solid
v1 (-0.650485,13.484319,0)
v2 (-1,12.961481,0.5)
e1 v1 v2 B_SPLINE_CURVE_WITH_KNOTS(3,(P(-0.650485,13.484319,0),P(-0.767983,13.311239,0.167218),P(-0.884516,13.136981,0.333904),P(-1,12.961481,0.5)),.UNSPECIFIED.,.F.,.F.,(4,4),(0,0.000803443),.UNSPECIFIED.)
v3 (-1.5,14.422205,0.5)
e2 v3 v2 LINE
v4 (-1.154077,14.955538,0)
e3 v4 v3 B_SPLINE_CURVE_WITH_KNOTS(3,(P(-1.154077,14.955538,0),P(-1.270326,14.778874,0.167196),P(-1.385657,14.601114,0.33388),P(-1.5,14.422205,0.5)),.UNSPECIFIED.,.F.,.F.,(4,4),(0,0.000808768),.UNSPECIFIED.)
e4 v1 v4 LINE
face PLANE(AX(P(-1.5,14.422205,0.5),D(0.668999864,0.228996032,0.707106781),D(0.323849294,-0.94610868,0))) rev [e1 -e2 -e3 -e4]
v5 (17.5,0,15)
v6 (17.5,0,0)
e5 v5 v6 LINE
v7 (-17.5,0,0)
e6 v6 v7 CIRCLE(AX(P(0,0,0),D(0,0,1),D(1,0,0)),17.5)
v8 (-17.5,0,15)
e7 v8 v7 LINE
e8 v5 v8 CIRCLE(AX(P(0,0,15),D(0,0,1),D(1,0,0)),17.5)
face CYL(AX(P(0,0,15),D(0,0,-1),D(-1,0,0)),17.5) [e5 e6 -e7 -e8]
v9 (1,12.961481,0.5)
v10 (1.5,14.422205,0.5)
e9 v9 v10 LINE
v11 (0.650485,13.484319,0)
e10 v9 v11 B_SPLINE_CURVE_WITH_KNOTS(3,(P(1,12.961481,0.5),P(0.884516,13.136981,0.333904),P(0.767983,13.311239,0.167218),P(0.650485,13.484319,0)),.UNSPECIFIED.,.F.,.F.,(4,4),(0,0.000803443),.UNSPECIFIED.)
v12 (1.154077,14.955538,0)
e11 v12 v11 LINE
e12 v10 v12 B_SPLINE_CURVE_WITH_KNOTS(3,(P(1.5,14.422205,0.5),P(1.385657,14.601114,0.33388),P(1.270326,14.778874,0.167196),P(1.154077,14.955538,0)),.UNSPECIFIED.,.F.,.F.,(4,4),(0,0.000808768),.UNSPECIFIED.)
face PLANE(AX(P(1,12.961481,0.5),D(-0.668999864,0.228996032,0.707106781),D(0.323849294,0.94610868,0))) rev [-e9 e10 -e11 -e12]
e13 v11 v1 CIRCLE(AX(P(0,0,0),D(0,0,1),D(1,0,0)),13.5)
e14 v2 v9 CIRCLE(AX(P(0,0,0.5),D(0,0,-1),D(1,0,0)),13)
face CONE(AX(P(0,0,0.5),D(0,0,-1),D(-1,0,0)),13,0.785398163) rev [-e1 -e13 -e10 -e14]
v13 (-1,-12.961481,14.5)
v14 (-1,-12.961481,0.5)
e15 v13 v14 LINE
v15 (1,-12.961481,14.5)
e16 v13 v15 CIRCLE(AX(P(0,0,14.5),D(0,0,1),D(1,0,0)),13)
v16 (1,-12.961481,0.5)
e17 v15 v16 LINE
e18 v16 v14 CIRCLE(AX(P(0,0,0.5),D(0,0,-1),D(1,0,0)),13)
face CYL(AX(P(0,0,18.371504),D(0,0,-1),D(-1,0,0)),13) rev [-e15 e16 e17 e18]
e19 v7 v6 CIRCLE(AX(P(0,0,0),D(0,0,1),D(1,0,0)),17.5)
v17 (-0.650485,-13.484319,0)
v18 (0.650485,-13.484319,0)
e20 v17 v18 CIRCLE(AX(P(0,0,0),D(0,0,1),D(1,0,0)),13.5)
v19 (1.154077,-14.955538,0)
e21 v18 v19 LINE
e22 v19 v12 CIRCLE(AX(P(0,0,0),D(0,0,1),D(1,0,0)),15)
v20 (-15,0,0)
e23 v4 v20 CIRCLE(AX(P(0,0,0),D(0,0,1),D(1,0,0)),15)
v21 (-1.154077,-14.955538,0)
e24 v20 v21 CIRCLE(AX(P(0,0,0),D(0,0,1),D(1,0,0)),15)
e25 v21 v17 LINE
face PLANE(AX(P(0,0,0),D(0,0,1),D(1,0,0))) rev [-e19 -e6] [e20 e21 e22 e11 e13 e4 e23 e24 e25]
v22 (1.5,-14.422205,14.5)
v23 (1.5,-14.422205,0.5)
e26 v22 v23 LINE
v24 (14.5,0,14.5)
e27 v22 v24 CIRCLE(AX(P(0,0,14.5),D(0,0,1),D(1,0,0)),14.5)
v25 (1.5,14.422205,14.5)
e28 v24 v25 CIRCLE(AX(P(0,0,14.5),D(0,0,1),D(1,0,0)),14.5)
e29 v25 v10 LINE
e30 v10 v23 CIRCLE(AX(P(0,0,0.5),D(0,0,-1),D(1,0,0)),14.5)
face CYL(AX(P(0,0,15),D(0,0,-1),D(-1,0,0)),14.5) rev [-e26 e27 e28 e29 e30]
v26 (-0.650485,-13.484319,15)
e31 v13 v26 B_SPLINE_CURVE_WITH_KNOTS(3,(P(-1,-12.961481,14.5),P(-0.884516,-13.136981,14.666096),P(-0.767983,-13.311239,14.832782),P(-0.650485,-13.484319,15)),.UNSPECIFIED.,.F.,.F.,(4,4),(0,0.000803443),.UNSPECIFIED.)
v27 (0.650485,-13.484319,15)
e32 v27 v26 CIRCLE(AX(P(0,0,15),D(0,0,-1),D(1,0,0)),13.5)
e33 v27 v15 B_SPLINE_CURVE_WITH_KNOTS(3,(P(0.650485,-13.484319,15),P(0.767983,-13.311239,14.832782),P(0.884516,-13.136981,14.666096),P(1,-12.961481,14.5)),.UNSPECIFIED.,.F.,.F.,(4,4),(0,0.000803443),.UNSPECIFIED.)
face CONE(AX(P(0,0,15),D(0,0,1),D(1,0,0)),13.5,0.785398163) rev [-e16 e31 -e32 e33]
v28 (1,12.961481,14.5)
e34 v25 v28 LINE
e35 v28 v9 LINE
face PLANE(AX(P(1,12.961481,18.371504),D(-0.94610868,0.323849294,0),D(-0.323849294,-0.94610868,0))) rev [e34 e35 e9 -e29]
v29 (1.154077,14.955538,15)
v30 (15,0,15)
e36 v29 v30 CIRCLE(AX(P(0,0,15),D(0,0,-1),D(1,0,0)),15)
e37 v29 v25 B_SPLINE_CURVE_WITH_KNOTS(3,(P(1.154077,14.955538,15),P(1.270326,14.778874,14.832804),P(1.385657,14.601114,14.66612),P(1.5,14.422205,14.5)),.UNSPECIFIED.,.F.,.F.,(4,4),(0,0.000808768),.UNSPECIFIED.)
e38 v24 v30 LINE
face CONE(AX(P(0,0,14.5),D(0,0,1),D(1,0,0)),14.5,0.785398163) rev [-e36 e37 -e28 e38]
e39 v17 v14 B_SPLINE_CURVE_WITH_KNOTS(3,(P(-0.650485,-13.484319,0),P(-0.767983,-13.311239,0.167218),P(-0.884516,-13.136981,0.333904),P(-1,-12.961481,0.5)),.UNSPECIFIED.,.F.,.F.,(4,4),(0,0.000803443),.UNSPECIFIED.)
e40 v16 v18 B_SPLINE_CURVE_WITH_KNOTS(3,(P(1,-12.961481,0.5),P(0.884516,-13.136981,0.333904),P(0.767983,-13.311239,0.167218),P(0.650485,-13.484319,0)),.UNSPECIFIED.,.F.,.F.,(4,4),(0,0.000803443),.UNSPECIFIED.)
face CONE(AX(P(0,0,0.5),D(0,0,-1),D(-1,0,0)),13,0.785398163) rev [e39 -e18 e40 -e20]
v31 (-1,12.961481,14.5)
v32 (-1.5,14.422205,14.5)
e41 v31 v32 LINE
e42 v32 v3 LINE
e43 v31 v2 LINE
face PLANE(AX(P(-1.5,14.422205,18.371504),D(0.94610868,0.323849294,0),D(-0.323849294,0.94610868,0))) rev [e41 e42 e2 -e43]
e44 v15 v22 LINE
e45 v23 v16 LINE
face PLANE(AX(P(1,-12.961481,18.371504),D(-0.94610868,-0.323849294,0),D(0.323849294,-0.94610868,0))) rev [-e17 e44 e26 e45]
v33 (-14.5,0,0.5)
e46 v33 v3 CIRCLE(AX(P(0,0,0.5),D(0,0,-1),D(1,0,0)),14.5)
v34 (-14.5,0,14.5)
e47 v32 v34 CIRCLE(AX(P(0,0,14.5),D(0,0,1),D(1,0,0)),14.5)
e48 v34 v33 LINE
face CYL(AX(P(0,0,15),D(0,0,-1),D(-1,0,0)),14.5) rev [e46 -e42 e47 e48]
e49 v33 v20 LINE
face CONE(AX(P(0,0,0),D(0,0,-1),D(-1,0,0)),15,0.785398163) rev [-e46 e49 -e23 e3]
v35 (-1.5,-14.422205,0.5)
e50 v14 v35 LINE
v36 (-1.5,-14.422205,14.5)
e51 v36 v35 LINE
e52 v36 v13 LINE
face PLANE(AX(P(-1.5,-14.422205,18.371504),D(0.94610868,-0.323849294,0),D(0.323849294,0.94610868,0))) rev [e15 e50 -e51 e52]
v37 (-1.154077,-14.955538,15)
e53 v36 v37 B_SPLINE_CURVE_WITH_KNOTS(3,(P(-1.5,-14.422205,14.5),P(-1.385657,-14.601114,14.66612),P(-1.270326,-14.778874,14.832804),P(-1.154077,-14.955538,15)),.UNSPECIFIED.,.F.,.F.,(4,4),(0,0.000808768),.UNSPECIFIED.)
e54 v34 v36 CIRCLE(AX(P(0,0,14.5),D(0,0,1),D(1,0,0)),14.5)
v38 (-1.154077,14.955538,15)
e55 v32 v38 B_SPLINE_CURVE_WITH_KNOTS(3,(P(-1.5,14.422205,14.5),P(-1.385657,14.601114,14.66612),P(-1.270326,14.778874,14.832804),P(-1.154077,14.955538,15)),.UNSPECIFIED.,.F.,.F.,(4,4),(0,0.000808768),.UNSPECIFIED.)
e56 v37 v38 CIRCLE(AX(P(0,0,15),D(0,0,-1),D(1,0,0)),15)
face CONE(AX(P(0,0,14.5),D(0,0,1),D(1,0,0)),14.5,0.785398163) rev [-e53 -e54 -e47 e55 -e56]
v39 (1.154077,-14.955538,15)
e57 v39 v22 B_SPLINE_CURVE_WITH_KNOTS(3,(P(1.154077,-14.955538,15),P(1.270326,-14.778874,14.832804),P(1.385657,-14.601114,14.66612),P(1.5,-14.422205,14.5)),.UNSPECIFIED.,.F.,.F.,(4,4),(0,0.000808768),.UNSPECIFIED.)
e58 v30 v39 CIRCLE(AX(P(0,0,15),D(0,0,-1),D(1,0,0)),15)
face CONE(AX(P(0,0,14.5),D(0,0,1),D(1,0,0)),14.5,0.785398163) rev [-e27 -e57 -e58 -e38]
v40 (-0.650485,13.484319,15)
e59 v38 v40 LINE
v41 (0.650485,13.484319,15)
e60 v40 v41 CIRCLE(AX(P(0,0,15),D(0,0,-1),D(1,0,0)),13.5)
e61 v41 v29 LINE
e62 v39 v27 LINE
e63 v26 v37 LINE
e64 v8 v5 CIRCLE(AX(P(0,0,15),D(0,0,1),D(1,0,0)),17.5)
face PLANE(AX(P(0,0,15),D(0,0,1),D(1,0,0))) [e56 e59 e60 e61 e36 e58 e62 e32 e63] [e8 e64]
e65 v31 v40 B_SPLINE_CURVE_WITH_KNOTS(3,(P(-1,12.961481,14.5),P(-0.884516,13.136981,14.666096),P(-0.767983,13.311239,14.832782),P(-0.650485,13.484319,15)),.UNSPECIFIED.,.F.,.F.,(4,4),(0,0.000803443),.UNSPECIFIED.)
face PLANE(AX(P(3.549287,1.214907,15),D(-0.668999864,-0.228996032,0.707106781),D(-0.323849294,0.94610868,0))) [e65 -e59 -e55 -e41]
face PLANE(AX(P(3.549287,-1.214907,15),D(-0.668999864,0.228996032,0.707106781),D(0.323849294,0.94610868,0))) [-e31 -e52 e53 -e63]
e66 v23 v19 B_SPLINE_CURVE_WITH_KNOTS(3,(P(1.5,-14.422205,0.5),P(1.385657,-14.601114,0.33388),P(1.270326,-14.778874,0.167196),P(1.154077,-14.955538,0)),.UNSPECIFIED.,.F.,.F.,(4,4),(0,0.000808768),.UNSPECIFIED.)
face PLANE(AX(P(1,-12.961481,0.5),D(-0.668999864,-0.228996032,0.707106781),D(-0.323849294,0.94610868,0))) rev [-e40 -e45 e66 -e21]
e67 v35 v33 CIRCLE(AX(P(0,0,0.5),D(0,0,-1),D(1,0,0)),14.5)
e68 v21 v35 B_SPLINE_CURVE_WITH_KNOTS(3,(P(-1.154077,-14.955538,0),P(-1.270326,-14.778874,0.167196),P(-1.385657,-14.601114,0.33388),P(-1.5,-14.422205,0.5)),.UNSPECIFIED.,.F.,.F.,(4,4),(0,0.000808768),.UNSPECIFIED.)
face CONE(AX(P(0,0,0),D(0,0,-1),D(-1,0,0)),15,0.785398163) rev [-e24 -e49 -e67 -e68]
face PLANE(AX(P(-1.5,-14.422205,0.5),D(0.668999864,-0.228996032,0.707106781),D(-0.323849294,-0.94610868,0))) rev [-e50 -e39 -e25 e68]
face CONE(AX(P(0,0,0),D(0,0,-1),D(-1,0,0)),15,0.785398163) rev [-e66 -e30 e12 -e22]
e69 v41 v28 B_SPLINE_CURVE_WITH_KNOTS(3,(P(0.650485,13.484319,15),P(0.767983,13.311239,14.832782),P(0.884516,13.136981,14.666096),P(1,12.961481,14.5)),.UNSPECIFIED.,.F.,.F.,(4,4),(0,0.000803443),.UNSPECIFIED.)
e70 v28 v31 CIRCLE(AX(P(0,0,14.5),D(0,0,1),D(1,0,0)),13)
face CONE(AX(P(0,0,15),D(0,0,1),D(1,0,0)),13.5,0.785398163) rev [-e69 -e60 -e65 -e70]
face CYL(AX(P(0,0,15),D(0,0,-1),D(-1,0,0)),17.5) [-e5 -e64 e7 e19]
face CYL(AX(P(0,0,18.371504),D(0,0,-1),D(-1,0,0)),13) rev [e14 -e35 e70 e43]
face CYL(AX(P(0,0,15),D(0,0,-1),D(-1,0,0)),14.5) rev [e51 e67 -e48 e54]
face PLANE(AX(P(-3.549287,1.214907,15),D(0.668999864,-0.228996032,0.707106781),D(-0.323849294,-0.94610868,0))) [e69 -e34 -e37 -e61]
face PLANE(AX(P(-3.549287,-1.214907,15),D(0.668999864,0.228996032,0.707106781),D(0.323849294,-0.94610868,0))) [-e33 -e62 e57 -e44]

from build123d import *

# Parameters (mm, degrees)
SKETCH2_R           = 17.5
SKETCH2_R_2         = 14.5
BOSS_EXTRUDE1_DEPTH = 15
BOSS_EXTRUDE2_DEPTH = 15
CHAMFER1_SIZE       = 0.5


with BuildPart() as part:
    # Sketch2 → Boss-Extrude1 (new body)
    with BuildSketch(Plane.XY):
        Circle(SKETCH2_R)
        Circle(SKETCH2_R_2, mode=Mode.SUBTRACT)
    extrude(amount=BOSS_EXTRUDE1_DEPTH)

    # Sketch4 → Boss-Extrude2 (add)
    with BuildSketch(Plane.XY):
        with BuildLine():
            Line((-1.5, 14.422205102), (-1, 12.961481397))
            ThreePointArc((-1, 12.961481397), (0, 13), (1, 12.961481397))
            Line((1, 12.961481397), (1.5, 14.422205102))
            ThreePointArc((1.5, 14.422205102), (0, 14.5), (-1.5, 14.422205102))
        make_face()
        with BuildLine():
            Line((1, -12.961481397), (1.5, -14.422205102))
            ThreePointArc((1.5, -14.422205102), (0, -14.5), (-1.5, -14.422205102))
            Line((-1.5, -14.422205102), (-1, -12.961481397))
            ThreePointArc((-1, -12.961481397), (0, -13), (1, -12.961481397))
        make_face()
    extrude(amount=BOSS_EXTRUDE2_DEPTH)

    # Chamfer1
    chamfer1_edges = [part.edges().sort_by_distance(p)[0] for p in [
        (-14.5, 0, 15),
        (-14.5, 0, 0),
        (-1.25, 13.691843249, 0),
        (0, 13, 0),
        (1.25, 13.691843249, 0),
        (1.25, 13.691843249, 15),
        (-1.25, 13.691843249, 15),
        (0, 13, 15),
        (14.5, 0, 0),
        (14.5, 0, 15),
        (1.25, -13.691843249, 0),
        (0, -13, 0),
        (-1.25, -13.691843249, 0),
        (-1.25, -13.691843249, 15),
        (1.25, -13.691843249, 15),
        (0, -13, 15),
    ]]
    chamfer(chamfer1_edges, length=CHAMFER1_SIZE)


solid = part.part
